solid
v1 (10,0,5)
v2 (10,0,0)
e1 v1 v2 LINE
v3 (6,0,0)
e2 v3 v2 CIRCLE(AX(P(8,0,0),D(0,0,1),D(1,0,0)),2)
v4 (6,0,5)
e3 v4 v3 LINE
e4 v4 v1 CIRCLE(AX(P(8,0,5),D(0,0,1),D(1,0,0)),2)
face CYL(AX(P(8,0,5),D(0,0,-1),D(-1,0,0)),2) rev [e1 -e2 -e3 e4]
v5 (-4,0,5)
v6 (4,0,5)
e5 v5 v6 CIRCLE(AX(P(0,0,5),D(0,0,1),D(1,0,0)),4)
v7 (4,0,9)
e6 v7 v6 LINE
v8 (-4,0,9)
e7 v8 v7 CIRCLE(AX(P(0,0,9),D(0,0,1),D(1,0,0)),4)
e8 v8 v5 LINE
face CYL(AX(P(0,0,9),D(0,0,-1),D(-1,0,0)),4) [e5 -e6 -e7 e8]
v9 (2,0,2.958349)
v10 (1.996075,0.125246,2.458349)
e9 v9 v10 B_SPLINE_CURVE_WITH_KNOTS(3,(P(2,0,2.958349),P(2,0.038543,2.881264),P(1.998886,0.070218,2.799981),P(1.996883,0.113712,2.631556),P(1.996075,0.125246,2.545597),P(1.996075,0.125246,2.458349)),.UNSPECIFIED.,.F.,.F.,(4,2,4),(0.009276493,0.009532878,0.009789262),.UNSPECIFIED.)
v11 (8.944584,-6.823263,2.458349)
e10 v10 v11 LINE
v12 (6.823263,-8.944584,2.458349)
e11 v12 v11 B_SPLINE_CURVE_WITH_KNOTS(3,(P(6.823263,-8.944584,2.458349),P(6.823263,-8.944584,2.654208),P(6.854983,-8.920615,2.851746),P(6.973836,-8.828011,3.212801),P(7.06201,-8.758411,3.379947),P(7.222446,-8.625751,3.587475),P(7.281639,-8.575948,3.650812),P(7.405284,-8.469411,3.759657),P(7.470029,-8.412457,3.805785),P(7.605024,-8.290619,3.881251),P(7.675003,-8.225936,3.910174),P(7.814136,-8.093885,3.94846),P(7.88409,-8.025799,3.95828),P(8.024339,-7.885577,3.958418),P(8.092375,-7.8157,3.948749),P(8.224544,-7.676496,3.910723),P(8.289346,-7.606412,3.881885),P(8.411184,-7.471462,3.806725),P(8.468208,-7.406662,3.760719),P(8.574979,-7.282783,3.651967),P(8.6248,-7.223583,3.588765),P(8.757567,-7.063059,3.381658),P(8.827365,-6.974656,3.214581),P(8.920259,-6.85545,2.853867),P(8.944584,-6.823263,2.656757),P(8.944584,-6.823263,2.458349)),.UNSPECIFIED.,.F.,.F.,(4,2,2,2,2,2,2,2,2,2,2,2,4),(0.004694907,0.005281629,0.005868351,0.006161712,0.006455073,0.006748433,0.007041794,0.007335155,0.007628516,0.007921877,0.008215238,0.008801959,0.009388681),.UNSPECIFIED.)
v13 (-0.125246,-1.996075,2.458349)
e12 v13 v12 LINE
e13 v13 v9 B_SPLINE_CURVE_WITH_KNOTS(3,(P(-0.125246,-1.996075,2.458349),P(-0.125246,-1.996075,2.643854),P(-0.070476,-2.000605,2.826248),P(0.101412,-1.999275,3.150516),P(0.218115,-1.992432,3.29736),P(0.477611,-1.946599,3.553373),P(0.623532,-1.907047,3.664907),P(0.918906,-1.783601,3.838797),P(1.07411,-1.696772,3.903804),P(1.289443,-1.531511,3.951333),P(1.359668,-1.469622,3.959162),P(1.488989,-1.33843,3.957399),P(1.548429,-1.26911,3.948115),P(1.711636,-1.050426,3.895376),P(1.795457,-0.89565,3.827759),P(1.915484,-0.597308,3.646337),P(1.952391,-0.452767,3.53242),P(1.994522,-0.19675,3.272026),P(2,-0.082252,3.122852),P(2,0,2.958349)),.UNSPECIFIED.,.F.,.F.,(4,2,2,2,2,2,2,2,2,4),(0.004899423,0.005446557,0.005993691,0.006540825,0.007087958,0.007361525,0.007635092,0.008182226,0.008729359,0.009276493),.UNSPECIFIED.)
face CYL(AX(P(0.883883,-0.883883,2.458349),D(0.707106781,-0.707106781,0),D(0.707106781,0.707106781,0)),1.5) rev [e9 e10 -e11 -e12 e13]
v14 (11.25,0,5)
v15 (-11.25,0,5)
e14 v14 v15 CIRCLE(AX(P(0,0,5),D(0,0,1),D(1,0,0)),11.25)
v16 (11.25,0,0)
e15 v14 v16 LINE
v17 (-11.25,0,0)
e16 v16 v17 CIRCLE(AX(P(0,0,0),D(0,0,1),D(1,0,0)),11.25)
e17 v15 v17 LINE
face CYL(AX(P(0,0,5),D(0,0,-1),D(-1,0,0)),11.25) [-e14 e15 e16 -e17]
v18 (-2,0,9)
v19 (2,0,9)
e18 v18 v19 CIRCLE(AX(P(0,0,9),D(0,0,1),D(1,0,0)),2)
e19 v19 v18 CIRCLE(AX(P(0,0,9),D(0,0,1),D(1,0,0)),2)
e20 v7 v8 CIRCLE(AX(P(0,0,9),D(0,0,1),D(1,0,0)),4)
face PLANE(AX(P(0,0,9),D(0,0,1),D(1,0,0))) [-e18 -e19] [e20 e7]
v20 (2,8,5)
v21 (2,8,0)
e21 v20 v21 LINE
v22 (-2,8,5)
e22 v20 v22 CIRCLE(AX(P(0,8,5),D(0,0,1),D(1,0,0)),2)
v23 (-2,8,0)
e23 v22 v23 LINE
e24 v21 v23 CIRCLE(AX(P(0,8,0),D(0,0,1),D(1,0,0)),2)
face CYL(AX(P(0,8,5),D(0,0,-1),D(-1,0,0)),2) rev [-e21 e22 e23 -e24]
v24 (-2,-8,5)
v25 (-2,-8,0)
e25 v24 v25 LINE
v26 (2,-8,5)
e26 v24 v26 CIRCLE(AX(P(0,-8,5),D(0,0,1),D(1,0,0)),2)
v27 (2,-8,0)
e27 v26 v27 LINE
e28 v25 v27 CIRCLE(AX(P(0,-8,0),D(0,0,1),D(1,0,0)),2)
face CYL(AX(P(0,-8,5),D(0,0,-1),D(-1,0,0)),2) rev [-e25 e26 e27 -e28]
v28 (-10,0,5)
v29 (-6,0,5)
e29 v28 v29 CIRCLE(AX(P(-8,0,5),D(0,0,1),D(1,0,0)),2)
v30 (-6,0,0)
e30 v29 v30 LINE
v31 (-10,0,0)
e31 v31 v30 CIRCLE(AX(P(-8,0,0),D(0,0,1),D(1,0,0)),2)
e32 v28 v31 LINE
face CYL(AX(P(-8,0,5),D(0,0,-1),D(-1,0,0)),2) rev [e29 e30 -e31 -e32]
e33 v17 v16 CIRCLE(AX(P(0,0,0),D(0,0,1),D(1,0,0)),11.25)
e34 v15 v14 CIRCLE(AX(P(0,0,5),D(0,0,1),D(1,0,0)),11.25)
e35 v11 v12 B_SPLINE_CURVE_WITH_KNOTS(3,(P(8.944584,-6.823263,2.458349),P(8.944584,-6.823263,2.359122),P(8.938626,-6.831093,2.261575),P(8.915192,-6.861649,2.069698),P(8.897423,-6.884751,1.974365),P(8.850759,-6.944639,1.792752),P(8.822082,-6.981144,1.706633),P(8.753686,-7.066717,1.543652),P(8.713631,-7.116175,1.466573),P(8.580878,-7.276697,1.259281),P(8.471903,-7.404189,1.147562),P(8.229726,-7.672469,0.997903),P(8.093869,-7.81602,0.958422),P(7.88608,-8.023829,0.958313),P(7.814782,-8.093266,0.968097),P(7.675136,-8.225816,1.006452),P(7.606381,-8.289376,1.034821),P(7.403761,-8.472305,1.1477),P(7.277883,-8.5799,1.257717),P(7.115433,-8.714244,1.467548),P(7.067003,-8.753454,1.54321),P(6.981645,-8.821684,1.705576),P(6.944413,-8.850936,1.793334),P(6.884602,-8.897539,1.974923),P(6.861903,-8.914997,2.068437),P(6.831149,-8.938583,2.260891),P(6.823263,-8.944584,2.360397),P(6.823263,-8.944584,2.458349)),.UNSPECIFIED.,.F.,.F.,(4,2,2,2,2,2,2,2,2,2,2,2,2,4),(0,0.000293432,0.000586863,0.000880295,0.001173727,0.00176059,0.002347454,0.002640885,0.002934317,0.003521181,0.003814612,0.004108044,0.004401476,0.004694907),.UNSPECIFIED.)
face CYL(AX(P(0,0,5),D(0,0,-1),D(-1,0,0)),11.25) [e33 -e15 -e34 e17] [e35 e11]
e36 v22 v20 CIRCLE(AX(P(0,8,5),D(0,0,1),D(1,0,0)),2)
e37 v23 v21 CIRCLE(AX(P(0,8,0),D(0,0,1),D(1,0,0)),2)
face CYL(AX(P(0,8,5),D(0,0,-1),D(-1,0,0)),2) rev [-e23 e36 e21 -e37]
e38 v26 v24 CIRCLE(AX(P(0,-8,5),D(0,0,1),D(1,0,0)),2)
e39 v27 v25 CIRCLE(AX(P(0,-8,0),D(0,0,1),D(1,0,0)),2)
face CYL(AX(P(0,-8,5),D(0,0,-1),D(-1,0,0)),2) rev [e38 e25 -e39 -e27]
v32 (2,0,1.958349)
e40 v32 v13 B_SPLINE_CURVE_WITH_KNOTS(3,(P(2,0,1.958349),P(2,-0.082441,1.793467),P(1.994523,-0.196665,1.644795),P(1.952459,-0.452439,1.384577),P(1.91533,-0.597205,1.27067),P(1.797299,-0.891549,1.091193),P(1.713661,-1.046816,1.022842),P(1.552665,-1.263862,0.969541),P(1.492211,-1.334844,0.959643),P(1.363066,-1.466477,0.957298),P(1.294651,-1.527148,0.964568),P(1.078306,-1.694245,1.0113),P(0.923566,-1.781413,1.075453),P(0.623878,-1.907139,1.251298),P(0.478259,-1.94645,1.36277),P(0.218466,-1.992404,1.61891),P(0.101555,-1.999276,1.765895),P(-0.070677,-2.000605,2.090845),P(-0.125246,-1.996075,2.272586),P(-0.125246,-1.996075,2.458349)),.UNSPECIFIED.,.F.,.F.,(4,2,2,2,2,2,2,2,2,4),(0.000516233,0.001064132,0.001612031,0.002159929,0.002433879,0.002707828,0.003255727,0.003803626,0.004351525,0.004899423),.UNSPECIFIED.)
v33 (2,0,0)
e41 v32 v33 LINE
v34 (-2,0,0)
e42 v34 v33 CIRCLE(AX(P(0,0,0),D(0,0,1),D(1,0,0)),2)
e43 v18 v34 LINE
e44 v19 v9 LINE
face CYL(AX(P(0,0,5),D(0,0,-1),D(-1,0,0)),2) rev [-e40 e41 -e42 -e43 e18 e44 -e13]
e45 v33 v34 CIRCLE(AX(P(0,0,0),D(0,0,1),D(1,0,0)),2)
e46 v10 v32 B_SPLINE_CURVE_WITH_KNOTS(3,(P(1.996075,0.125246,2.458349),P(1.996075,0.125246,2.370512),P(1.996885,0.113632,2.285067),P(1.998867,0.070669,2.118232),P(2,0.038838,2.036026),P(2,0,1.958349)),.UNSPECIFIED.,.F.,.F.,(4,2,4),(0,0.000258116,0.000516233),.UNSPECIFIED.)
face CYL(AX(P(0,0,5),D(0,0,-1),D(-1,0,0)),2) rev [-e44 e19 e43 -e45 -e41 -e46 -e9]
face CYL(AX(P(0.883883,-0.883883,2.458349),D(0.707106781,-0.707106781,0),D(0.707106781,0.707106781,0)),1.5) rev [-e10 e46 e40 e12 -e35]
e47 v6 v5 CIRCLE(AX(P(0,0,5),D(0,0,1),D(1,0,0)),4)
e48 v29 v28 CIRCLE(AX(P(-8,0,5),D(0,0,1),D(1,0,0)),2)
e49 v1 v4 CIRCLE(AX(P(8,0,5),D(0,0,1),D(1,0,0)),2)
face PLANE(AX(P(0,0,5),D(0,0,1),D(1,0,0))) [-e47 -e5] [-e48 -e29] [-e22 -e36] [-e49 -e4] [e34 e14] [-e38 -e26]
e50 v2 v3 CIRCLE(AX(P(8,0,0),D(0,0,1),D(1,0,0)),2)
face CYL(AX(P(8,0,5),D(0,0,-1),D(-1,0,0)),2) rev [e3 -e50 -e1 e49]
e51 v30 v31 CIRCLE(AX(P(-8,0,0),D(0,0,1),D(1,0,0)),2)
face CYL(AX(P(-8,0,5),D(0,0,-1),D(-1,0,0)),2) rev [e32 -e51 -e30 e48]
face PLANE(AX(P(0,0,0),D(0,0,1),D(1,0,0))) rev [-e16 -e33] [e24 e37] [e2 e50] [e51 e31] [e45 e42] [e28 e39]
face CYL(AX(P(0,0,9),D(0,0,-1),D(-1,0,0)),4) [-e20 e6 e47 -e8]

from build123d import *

# Parameters (mm, degrees)
SKETCH1_R           = 11.25
SKETCH1_R_2         = 2
BOSS_EXTRUDE1_DEPTH = 5
SKETCH2_R           = 4
SKETCH2_R_2         = 2
BOSS_EXTRUDE2_DEPTH = 4
CUT_EXTRUDE1_DEPTH  = 10


with BuildPart() as part:
    # Sketch1 → Boss-Extrude1 (new body)
    with BuildSketch(Plane.XY):
        Circle(SKETCH1_R)
        with Locations((0, 8)):
            Circle(SKETCH1_R_2, mode=Mode.SUBTRACT)
        with Locations((8, 0)):
            Circle(SKETCH1_R_2, mode=Mode.SUBTRACT)
        with Locations((0, -8)):
            Circle(SKETCH1_R_2, mode=Mode.SUBTRACT)
        with Locations((-8, 0)):
            Circle(SKETCH1_R_2, mode=Mode.SUBTRACT)
        Circle(SKETCH1_R_2, mode=Mode.SUBTRACT)
    extrude(amount=BOSS_EXTRUDE1_DEPTH)

    # Sketch2 → Boss-Extrude2 (add)
    with BuildSketch(Plane.XY.offset(5)):
        Circle(SKETCH2_R)
        Circle(SKETCH2_R_2, mode=Mode.SUBTRACT)
    extrude(amount=BOSS_EXTRUDE2_DEPTH)

    # Sketch4 → Cut-Extrude1 (cut)
    with BuildSketch(Plane(origin=(7.954951288, -7.954951288, 0), x_dir=(-0.7071067811865475, -0.7071067811865477, 0), z_dir=(0.7071067811865477, -0.7071067811865475, 0))):
        with BuildLine():
            ThreePointArc((1.5, -2.45834938), (1.060660172, -1.397689208), (0, -0.95834938))
            Line((0, -0.95834938), (0, -3.95834938))
            ThreePointArc((0, -3.95834938), (1.060660172, -3.519009552), (1.5, -2.45834938))
        make_face()
        with BuildLine():
            Line((0, -3.95834938), (0, -0.95834938))
            ThreePointArc((0, -0.95834938), (-1.5, -2.45834938), (0, -3.95834938))
        make_face()
    extrude(amount=-CUT_EXTRUDE1_DEPTH, mode=Mode.SUBTRACT)


solid = part.part
